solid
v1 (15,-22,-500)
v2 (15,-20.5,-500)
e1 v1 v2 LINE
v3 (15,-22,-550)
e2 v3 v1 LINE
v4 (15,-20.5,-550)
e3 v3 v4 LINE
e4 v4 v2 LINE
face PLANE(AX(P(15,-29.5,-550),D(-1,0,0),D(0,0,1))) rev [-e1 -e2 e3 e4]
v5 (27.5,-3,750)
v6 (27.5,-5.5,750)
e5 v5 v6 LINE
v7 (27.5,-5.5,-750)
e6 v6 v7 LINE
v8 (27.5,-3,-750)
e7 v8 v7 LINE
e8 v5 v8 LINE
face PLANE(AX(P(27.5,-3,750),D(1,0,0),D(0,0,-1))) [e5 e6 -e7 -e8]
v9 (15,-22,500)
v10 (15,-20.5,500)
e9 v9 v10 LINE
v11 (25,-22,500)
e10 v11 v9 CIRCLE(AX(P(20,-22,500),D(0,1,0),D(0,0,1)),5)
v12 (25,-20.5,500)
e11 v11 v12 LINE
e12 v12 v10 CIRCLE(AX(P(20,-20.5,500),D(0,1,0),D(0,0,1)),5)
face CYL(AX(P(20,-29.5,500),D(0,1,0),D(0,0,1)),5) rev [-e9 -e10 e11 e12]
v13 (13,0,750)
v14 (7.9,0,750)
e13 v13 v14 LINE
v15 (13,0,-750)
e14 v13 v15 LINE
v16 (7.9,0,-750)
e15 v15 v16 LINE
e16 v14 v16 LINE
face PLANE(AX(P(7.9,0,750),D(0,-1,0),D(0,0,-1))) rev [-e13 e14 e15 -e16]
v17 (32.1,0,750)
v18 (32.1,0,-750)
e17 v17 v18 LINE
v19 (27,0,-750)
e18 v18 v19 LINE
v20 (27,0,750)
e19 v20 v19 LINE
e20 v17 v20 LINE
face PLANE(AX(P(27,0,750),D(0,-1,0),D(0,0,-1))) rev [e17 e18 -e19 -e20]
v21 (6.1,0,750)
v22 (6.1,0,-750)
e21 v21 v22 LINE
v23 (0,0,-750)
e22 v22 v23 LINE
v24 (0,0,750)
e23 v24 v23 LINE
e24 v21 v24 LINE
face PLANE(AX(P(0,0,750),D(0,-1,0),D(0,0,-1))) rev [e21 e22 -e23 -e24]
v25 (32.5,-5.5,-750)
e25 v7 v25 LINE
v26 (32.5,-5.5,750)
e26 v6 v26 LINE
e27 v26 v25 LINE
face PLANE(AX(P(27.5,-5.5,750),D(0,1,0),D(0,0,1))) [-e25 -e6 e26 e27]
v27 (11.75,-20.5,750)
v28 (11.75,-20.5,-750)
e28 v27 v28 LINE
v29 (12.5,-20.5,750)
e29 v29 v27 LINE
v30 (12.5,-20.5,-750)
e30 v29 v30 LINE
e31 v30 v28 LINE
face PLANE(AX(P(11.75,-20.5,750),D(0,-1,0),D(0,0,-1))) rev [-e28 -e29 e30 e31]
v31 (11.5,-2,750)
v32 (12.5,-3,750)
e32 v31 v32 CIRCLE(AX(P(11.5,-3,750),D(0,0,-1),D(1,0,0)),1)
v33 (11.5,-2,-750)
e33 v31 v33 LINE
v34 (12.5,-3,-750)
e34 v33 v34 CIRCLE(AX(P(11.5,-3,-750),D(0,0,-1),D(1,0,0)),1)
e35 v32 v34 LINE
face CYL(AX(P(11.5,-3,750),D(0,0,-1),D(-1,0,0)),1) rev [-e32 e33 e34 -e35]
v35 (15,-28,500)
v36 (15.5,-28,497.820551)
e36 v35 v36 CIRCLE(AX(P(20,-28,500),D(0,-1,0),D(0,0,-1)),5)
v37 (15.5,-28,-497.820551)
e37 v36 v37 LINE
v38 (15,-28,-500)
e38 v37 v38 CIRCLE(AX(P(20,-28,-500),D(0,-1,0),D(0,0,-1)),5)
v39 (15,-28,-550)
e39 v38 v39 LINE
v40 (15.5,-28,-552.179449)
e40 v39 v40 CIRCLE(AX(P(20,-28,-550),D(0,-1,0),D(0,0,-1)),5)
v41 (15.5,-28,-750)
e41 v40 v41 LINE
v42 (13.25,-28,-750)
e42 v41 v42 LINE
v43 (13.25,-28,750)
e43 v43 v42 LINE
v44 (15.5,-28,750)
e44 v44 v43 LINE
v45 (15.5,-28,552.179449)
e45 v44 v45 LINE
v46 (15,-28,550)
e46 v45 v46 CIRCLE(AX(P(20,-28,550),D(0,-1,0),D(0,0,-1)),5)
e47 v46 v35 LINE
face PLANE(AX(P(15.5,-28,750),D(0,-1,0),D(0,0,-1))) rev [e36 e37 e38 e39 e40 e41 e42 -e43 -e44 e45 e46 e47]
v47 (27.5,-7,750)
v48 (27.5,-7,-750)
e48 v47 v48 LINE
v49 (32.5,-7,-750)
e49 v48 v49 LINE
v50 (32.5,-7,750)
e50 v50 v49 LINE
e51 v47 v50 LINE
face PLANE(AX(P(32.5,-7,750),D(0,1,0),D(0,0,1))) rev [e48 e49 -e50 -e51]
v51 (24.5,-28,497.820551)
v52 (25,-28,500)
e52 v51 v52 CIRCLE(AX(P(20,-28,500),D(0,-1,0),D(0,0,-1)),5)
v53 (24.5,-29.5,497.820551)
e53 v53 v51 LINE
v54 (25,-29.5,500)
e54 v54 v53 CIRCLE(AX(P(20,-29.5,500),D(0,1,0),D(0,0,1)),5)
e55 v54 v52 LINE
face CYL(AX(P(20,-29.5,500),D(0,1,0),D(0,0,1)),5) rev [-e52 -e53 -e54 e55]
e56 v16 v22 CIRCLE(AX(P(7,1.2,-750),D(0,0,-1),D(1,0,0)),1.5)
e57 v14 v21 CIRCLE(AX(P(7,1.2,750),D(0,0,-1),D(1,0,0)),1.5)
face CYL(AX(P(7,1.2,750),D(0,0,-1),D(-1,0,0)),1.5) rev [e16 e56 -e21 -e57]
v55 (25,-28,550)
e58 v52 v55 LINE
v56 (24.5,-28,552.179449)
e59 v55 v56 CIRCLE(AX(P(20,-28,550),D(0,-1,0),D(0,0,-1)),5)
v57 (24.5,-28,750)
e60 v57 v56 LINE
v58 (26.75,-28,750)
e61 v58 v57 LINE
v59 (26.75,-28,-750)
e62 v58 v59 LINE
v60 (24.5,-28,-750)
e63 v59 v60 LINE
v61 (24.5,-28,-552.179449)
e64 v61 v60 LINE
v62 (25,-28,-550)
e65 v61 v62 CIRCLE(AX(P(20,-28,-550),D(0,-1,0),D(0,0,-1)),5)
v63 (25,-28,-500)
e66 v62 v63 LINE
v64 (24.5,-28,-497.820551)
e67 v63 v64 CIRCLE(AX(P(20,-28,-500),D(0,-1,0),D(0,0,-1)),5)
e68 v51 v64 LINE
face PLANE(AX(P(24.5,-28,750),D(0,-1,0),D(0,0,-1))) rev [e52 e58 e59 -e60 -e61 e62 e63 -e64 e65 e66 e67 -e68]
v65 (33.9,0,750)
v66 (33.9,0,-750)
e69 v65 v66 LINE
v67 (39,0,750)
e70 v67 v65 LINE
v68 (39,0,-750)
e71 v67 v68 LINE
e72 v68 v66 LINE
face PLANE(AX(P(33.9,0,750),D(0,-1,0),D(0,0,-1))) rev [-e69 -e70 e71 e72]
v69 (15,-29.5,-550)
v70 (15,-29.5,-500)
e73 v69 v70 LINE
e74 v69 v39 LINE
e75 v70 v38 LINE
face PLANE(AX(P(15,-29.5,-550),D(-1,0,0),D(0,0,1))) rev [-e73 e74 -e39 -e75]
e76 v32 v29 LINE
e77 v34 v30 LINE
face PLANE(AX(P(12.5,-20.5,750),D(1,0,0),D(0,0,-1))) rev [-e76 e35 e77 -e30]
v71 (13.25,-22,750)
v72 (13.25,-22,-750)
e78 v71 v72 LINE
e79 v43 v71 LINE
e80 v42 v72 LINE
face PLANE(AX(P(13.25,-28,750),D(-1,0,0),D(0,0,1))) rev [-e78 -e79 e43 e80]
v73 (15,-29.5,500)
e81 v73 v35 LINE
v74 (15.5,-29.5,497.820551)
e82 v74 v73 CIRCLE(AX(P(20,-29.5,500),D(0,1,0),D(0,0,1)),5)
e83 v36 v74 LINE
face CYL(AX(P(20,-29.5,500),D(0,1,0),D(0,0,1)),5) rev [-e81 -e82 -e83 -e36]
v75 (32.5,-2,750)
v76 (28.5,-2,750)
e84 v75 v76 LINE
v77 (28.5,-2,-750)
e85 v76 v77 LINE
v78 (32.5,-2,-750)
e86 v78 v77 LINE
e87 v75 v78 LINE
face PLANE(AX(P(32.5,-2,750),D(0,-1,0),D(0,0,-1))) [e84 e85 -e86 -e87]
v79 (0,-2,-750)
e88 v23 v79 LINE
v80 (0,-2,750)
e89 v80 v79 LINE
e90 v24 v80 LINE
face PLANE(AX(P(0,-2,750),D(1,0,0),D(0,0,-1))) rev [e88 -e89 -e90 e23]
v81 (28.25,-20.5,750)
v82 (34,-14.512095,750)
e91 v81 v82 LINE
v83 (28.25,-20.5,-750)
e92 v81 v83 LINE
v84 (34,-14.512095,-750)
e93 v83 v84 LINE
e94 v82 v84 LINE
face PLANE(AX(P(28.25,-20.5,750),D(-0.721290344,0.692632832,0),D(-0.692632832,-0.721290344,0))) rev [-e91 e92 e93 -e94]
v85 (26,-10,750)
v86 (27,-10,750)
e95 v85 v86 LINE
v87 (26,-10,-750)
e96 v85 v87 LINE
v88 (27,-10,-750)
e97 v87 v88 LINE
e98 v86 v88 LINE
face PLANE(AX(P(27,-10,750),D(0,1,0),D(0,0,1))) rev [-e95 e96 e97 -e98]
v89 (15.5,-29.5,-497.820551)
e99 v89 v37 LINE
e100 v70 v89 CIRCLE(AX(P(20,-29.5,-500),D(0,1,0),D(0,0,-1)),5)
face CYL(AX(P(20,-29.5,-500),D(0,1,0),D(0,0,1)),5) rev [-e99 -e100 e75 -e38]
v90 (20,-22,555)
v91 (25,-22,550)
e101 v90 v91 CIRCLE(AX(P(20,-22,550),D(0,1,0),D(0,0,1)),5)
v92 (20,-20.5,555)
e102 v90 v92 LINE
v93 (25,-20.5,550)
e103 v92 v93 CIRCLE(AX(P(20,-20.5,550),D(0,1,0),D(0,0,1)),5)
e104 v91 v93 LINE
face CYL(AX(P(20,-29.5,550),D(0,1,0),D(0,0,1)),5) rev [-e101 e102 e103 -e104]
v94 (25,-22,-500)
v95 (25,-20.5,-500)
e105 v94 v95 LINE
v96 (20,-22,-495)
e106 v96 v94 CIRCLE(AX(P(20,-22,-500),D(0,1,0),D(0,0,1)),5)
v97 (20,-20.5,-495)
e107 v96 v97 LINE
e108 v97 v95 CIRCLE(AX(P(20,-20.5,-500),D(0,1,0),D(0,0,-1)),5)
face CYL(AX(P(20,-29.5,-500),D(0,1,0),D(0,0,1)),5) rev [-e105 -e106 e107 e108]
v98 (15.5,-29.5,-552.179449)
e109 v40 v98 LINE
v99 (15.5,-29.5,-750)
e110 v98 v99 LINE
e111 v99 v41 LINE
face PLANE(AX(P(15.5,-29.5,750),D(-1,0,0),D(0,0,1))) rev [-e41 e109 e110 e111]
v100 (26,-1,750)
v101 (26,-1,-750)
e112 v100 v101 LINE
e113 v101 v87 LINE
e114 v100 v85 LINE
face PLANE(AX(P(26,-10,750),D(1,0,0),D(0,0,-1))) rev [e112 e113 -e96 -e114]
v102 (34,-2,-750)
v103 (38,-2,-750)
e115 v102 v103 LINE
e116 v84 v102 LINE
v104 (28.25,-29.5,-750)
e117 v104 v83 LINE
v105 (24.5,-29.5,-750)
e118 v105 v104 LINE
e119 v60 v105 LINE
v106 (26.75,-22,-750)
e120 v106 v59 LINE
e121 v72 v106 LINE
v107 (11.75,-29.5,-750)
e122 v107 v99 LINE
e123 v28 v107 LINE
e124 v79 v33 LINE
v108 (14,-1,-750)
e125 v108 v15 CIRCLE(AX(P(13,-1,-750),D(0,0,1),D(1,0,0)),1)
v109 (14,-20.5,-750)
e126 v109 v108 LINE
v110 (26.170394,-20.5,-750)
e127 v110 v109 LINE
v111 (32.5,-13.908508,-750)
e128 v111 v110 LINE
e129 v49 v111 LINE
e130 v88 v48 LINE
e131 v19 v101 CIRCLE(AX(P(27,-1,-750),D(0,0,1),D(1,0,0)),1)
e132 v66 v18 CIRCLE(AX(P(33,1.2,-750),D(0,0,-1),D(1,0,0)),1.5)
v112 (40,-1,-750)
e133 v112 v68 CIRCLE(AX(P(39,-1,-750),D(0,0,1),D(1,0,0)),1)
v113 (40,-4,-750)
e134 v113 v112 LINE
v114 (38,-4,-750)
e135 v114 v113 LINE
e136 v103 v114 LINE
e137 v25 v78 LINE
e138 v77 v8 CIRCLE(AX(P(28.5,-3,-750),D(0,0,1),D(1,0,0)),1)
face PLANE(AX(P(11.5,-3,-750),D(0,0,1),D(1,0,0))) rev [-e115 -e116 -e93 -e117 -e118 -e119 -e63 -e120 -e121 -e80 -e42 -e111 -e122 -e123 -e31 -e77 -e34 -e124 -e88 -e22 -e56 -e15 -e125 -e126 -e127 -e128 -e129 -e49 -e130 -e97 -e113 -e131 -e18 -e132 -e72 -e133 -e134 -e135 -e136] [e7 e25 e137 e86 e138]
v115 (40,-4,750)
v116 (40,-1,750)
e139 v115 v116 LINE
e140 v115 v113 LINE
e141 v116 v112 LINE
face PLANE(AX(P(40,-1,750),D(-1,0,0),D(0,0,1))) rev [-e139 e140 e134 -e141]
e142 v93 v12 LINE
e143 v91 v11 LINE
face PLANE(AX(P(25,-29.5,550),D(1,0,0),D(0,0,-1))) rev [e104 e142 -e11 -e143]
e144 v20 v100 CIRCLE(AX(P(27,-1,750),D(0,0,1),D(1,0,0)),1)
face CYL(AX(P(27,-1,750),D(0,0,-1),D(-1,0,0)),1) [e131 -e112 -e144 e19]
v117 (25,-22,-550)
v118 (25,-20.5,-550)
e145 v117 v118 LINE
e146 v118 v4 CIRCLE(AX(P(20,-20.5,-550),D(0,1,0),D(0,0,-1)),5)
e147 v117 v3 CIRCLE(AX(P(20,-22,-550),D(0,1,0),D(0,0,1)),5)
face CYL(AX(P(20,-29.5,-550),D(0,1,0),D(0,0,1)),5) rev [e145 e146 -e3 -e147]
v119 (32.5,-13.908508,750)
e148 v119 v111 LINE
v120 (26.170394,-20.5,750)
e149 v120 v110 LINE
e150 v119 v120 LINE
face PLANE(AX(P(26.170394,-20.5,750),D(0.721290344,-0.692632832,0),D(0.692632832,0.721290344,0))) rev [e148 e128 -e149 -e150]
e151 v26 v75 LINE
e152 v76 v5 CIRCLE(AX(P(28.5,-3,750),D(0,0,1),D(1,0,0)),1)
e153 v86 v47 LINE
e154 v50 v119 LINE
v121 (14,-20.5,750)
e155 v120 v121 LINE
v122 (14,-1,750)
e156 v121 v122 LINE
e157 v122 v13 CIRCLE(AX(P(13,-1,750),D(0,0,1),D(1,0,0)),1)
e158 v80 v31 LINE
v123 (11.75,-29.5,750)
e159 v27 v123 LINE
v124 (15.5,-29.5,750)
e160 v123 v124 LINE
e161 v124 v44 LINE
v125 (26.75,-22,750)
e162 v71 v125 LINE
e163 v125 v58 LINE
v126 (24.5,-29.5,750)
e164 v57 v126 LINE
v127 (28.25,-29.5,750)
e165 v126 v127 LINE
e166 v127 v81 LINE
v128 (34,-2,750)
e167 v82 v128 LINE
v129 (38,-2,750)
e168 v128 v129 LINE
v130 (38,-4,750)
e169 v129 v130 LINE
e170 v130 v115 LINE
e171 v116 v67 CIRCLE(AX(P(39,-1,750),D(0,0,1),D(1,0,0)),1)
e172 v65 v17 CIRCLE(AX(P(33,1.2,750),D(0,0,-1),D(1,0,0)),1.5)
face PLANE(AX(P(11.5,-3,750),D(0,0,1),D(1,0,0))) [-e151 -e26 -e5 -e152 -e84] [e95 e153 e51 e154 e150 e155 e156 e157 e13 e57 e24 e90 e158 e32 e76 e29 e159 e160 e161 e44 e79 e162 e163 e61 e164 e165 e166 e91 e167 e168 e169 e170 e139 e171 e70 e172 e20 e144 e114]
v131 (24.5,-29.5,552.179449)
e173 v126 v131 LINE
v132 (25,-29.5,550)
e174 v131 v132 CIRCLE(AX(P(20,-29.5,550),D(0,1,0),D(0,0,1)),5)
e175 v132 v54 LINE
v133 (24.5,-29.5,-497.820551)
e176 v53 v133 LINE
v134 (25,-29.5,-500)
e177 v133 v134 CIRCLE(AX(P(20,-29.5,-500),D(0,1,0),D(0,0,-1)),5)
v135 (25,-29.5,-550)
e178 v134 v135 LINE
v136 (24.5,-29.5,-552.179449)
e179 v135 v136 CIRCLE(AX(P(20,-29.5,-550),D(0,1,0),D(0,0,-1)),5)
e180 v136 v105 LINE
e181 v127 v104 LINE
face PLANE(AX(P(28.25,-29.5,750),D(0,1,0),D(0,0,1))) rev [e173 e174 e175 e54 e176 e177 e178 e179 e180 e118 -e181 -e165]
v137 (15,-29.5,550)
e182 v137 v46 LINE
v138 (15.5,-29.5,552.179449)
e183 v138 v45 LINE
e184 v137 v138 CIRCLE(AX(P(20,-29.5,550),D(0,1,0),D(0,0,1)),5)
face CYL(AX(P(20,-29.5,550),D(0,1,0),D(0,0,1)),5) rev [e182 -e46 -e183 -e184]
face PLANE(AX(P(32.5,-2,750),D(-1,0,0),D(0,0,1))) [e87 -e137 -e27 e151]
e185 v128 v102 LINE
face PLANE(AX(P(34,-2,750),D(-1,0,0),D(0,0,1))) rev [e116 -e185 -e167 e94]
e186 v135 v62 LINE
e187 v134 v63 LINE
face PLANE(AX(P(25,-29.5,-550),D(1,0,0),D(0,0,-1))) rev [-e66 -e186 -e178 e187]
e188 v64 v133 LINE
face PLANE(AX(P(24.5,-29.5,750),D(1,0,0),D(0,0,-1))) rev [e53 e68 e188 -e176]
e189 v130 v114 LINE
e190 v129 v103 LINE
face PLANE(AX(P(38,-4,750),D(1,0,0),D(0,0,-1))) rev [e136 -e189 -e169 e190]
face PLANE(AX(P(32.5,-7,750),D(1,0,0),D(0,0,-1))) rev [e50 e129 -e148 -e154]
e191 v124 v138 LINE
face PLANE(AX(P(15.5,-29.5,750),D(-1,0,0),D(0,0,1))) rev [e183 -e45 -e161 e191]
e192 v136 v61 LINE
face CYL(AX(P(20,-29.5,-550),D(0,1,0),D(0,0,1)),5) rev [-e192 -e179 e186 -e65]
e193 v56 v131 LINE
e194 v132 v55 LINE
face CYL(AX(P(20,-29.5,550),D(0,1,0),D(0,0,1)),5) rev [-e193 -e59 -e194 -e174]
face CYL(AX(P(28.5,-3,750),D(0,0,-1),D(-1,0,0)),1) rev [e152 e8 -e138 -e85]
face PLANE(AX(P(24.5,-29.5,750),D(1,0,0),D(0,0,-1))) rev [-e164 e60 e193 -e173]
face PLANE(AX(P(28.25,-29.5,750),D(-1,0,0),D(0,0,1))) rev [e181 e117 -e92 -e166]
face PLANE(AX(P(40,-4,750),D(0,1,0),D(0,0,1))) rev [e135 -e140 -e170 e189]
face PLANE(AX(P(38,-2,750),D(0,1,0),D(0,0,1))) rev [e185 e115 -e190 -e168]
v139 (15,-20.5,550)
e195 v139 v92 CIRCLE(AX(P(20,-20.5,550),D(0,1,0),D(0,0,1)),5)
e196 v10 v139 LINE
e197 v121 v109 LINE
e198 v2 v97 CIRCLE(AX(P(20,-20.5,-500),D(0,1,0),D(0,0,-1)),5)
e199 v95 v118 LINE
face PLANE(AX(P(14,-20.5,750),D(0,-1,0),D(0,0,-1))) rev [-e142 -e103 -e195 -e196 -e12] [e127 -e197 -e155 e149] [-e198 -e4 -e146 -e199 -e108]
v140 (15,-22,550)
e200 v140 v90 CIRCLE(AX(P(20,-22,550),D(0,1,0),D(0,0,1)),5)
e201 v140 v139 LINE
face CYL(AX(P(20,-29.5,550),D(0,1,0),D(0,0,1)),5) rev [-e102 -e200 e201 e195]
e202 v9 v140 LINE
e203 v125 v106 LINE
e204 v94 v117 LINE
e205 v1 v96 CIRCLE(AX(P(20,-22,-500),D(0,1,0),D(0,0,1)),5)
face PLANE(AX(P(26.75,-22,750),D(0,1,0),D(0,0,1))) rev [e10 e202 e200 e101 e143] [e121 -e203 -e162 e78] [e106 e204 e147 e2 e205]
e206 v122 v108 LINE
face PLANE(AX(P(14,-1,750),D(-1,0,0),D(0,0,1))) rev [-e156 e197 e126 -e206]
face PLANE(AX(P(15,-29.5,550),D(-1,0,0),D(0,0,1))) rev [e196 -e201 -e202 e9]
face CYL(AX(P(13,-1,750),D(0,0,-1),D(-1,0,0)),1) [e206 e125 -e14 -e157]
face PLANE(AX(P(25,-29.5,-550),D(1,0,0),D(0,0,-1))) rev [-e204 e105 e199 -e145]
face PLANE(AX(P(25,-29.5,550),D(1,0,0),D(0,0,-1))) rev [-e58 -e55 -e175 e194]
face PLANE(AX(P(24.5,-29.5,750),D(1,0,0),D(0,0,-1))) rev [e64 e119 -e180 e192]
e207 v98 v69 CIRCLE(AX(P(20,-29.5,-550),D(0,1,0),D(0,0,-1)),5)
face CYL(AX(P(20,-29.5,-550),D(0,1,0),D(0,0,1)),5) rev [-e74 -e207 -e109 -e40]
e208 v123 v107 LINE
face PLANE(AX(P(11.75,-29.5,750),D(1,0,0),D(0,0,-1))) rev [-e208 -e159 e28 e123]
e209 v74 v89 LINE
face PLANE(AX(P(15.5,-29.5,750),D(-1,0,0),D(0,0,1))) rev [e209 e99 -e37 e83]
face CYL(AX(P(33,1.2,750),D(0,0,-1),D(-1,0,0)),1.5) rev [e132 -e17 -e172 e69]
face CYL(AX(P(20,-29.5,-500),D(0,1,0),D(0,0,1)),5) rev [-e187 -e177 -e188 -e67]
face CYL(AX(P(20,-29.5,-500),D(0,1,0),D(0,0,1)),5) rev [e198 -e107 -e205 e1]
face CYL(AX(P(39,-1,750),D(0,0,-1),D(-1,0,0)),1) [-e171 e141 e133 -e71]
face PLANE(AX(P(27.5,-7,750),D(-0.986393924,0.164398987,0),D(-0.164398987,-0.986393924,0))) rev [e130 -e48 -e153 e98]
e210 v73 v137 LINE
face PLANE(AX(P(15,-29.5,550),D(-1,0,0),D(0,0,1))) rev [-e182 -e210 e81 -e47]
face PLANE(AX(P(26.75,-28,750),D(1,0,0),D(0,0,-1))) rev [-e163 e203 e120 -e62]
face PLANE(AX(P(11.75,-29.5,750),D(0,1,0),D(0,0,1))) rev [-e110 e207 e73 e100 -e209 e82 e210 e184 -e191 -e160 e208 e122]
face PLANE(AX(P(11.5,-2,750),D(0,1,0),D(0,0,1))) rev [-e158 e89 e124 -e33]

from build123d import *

# Parameters (mm, degrees)
EXTRUDE_1_DEPTH     = 750
CUT_EXTRUDE_1_DEPTH = 752.345626193


with BuildPart() as part:
    # 草图1 → 凸台-拉伸1 (new, symmetric)
    with BuildSketch(Plane.XY):
        with BuildLine():
            Line((11.75, -20.5), (12.5, -20.5))
            Line((12.5, -20.5), (12.5, -3))
            ThreePointArc((12.5, -3), (12.207106781, -2.292893219), (11.5, -2))
            Line((11.5, -2), (0, -2))
            Line((0, -2), (0, 0))
            Line((0, 0), (6.1, 0))
            ThreePointArc((6.1, 0), (7, -0.3), (7.9, 0))
            Line((7.9, 0), (13, 0))
            ThreePointArc((13, 0), (13.707106781, -0.292893219), (14, -1))
            Line((14, -1), (14, -20.5))
            Line((14, -20.5), (26.170393622, -20.5))
            Line((26.170393622, -20.5), (32.5, -13.908507718))
            Line((32.5, -13.908507718), (32.5, -7))
            Line((32.5, -7), (27.5, -7))
            Line((27.5, -7), (27, -10))
            Line((27, -10), (26, -10))
            Line((26, -10), (26, -1))
            ThreePointArc((26, -1), (26.292893219, -0.292893219), (27, 0))
            Line((27, 0), (32.1, 0))
            ThreePointArc((32.1, 0), (33, -0.3), (33.9, 0))
            Line((33.9, 0), (39, 0))
            ThreePointArc((39, 0), (39.707106781, -0.292893219), (40, -1))
            Line((40, -1), (40, -4))
            Line((40, -4), (38, -4))
            Line((38, -4), (38, -2))
            Line((38, -2), (34, -2))
            Line((34, -2), (34, -14.512095167))
            Line((34, -14.512095167), (28.25, -20.5))
            Line((28.25, -20.5), (28.25, -29.5))
            Line((28.25, -29.5), (24.5, -29.5))
            Line((24.5, -29.5), (24.5, -28))
            Line((24.5, -28), (26.75, -28))
            Line((26.75, -28), (26.75, -22))
            Line((26.75, -22), (13.25, -22))
            Line((13.25, -22), (13.25, -28))
            Line((13.25, -28), (15.5, -28))
            Line((15.5, -28), (15.5, -29.5))
            Line((15.5, -29.5), (11.75, -29.5))
            Line((11.75, -29.5), (11.75, -20.5))
        make_face()
        with BuildLine():
            Line((32.5, -2), (32.5, -5.5))
            Line((32.5, -5.5), (27.5, -5.5))
            Line((27.5, -5.5), (27.5, -3))
            ThreePointArc((27.5, -3), (27.792893219, -2.292893219), (28.5, -2))
            Line((28.5, -2), (32.5, -2))
        make_face(mode=Mode.SUBTRACT)
    extrude(amount=EXTRUDE_1_DEPTH, both=True)

    # 草图2 → 切除-拉伸1 (cut, through all)
    with BuildSketch(Plane(origin=(0, -20.5, 0), x_dir=(1, 0, 0), z_dir=(0, 1, 0))):
        with BuildLine():
            Line((15, -550), (15, -500))
            ThreePointArc((15, -500), (20, -495), (25, -500))
            Line((25, -500), (25, -550))
            ThreePointArc((25, -550), (20, -555), (15, -550))
        make_face()
        with BuildLine():
            Line((15, 550), (15, 500))
            ThreePointArc((15, 500), (20, 495), (25, 500))
            Line((25, 500), (25, 550))
            ThreePointArc((25, 550), (20, 555), (15, 550))
        make_face()
    extrude(amount=-CUT_EXTRUDE_1_DEPTH, mode=Mode.SUBTRACT)


solid = part.part
